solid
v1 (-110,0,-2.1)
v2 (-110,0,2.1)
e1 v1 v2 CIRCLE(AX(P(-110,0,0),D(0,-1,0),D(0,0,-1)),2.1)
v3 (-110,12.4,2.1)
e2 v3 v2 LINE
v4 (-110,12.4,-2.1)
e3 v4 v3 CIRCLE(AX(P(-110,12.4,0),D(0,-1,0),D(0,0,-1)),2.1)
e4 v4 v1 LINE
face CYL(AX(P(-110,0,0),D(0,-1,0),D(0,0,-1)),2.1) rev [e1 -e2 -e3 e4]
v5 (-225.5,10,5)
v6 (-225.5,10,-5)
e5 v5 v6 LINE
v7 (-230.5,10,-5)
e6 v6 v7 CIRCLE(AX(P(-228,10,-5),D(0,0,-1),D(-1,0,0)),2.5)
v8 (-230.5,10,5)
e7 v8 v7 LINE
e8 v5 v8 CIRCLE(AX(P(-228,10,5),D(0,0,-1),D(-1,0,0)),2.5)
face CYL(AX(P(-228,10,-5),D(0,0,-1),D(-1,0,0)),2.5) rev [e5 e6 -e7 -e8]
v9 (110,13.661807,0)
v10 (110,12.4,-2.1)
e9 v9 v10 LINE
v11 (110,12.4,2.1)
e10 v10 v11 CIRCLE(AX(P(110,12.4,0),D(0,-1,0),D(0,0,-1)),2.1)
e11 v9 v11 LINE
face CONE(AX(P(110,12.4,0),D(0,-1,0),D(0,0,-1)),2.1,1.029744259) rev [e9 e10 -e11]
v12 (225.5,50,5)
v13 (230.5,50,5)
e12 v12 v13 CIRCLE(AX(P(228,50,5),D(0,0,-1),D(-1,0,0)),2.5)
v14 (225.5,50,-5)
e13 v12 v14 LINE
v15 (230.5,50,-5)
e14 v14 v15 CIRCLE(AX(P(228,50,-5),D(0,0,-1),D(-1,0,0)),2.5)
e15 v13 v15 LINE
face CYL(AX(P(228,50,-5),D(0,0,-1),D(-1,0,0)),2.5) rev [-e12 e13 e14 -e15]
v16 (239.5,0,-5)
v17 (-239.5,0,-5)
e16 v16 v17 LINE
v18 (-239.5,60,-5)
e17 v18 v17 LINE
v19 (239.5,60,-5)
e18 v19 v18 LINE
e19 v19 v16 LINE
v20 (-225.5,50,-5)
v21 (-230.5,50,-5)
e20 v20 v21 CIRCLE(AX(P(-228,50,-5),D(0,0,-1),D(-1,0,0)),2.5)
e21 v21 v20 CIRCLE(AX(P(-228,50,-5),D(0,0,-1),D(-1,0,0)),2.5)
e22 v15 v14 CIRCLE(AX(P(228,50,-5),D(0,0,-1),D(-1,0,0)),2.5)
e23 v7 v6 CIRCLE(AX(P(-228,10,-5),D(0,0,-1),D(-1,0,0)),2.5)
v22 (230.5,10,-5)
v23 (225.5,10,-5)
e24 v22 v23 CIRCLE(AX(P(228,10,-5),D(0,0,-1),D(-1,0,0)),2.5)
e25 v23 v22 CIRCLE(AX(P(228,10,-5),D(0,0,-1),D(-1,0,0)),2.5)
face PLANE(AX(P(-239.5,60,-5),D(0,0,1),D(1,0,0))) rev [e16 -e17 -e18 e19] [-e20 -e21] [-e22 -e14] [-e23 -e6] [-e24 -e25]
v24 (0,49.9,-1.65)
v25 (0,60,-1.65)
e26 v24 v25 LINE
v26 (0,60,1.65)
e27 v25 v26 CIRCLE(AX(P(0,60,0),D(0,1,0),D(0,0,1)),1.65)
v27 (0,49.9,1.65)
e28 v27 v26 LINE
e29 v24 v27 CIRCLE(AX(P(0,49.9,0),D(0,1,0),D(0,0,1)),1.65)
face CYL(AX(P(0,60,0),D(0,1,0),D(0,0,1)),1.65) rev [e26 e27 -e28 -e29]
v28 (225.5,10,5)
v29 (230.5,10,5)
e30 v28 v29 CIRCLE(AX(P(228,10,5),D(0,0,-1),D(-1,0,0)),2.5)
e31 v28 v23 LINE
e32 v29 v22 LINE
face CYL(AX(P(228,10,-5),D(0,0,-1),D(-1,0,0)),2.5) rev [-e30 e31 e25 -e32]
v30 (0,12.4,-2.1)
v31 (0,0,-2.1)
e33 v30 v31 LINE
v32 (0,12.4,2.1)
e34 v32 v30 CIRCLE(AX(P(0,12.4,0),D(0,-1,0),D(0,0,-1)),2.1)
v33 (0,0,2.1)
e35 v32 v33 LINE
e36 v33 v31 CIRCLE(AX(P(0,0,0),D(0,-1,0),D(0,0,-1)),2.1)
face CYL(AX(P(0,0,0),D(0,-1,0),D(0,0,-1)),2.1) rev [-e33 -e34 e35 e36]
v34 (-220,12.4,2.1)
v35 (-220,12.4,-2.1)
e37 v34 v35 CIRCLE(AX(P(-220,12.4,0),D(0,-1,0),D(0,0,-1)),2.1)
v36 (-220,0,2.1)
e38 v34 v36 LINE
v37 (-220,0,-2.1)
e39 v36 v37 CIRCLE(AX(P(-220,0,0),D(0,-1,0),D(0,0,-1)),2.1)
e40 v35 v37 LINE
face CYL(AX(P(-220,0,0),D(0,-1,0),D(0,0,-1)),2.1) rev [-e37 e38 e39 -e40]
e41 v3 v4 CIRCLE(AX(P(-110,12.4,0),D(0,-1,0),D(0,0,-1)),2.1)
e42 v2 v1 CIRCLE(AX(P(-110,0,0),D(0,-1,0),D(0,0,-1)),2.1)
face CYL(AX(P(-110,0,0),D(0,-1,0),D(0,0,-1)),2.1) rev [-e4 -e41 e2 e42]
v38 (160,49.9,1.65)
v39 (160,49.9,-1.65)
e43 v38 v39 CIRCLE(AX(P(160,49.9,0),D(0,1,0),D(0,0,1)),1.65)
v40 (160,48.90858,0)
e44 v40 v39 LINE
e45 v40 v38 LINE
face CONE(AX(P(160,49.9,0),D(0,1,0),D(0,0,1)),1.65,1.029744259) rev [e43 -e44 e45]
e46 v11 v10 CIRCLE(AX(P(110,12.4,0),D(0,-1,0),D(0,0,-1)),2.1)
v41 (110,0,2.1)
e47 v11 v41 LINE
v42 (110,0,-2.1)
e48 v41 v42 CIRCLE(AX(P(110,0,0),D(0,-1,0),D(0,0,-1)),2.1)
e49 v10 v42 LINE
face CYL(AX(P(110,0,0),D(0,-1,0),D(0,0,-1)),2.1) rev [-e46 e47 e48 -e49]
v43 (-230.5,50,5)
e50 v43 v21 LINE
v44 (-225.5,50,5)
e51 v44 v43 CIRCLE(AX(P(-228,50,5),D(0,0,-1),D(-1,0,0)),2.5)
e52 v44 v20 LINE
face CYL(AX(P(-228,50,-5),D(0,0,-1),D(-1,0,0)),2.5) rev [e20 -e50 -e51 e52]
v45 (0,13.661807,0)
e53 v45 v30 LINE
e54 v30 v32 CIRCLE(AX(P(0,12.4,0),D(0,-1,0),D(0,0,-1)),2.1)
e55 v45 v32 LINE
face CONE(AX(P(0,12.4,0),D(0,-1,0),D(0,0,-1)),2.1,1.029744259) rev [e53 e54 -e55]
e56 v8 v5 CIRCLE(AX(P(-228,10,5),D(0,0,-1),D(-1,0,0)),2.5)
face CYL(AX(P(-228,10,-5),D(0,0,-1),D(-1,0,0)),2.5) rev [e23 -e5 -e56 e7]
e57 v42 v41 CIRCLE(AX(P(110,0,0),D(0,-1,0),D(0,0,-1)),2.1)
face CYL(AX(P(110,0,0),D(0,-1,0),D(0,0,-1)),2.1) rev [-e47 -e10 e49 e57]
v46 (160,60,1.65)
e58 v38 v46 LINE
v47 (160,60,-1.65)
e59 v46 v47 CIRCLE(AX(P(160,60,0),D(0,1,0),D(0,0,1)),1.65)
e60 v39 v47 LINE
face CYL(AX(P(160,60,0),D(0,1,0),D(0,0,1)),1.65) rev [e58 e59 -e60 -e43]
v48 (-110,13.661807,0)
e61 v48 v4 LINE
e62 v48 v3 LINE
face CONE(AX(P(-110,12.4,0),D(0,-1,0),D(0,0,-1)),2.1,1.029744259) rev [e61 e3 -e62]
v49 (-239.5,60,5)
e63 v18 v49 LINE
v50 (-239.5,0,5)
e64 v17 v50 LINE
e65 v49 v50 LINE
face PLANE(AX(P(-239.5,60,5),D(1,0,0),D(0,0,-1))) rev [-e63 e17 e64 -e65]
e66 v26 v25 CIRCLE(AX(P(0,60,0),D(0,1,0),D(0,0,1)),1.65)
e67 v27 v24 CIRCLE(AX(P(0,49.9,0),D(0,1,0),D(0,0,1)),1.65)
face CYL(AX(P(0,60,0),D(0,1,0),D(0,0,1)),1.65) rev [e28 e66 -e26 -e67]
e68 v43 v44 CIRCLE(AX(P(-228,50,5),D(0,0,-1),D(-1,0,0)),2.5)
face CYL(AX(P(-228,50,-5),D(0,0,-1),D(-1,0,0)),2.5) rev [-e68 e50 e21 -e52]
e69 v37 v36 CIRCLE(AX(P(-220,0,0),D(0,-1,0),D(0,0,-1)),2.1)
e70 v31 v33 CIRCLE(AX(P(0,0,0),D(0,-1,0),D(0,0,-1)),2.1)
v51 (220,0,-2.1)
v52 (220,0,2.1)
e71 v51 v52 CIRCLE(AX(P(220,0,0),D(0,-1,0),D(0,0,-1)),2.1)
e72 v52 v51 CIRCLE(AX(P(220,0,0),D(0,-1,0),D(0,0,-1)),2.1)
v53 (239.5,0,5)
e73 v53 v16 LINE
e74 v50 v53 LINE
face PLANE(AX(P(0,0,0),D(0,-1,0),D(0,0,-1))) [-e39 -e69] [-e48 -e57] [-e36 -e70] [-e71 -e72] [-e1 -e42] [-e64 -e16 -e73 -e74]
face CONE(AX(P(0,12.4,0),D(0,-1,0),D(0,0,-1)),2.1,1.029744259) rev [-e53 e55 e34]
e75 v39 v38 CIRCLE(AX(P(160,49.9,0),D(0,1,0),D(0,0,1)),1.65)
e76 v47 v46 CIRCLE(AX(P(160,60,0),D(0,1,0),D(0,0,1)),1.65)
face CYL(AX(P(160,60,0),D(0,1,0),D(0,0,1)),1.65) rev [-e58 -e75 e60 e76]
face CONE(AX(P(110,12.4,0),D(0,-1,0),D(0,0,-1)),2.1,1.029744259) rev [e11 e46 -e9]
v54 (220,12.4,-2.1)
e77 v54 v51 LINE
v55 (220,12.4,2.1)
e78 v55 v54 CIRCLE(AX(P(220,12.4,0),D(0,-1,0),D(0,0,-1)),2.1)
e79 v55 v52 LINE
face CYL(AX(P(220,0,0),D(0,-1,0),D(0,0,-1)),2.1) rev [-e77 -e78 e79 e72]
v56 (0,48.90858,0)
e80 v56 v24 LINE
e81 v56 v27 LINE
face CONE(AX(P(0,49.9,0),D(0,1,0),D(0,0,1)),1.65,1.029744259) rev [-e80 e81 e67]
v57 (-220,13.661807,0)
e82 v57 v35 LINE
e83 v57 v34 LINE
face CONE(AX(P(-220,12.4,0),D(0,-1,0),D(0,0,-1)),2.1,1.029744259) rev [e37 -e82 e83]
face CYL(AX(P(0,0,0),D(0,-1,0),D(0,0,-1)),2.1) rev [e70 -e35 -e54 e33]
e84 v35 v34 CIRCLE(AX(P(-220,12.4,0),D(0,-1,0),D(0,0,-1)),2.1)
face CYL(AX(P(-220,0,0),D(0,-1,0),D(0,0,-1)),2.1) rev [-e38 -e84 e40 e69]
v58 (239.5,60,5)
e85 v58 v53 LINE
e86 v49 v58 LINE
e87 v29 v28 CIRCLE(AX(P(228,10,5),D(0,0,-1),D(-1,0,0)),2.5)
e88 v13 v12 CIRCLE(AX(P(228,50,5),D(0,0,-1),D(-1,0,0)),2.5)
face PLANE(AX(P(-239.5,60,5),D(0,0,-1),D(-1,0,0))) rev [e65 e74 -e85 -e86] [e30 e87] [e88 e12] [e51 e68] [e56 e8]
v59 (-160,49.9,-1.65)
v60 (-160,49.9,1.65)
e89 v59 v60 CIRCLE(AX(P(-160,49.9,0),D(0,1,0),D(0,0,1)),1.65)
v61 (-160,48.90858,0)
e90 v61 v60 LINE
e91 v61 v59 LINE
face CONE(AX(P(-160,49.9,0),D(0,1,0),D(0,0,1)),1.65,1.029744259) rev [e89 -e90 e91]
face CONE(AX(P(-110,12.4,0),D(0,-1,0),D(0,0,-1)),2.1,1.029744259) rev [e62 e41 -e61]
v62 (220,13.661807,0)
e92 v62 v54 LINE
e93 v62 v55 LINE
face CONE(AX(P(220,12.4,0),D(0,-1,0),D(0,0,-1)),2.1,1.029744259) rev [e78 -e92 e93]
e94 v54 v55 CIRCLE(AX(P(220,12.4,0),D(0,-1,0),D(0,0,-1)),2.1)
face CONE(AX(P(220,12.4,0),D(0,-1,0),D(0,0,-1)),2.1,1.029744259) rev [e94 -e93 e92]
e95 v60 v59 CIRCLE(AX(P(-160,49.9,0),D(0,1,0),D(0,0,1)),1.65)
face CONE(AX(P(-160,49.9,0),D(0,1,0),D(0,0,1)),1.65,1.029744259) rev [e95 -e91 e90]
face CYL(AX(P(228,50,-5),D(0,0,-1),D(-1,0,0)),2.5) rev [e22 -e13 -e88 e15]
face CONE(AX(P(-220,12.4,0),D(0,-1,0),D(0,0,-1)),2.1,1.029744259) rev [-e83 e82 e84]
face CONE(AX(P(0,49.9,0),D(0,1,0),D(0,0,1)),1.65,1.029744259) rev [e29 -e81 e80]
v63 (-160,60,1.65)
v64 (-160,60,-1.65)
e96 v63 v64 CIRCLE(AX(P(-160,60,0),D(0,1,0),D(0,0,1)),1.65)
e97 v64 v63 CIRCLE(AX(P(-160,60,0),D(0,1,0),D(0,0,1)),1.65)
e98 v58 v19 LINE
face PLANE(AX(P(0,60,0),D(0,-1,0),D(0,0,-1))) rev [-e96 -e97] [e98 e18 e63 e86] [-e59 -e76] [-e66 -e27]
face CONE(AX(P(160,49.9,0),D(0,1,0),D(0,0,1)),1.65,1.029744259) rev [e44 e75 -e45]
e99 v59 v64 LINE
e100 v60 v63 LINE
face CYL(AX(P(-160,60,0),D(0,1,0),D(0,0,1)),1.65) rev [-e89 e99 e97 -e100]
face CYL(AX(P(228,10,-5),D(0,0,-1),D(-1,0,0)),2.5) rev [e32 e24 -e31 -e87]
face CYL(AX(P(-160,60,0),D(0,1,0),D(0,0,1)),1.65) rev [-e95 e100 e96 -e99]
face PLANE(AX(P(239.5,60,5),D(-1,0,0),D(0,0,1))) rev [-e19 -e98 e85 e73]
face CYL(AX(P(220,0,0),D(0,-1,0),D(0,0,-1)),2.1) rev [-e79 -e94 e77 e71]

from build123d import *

# Parameters (mm, degrees)
SKETCH_1_W             = 479
SKETCH_1_H             = 10
EXTRUDE_1_DEPTH        = 60
HOLE_WIZARD_M5_1_D     = 4.2
HOLE_WIZARD_M5_1_DEPTH = 12.4
HOLE_WIZARD_M5_1_TIP   = 1.2618073
HOLE_WIZARD_M6_1_D     = 5
HOLE_WIZARD_M4_1_D     = 3.3
HOLE_WIZARD_M4_1_DEPTH = 10.1
HOLE_WIZARD_M4_1_TIP   = 0.991420021


with BuildPart() as part:
    # 草图1 → 凸台-拉伸1 (new body)
    with BuildSketch(Plane(origin=(0, 0, 0), x_dir=(1, 0, 0), z_dir=(0, 1, 0))):
        Rectangle(SKETCH_1_W, SKETCH_1_H)
    extrude(amount=EXTRUDE_1_DEPTH)

    # M5 螺纹孔1
    with Locations(Plane(origin=(0, 0, 0), x_dir=(-1, 0, 0), z_dir=(0, -1, 0))):
        with Locations((0, 0), (-110, 0), (-220, 0), (220, 0), (110, 0)):
            Hole(HOLE_WIZARD_M5_1_D / 2, depth=HOLE_WIZARD_M5_1_DEPTH)
            with Locations((0, 0, -(HOLE_WIZARD_M5_1_DEPTH + HOLE_WIZARD_M5_1_TIP / 2))):  # 118° drill point
                Cone(0, HOLE_WIZARD_M5_1_D / 2, HOLE_WIZARD_M5_1_TIP, mode=Mode.SUBTRACT)

    # M6 螺纹孔1 (through all)
    with Locations(Plane(origin=(0, 0, -5), x_dir=(-1, 0, 0), z_dir=(0, 0, -1))):
        with Locations((228, 50), (228, 10), (-228, 10), (-228, 50)):
            Hole(HOLE_WIZARD_M6_1_D / 2)

    # M4 螺纹孔1
    with Locations(Plane(origin=(0, 60, 0), x_dir=(1, 0, 0), z_dir=(0, 1, 0))):
        with Locations((0, 0), (-160, 0), (160, 0)):
            Hole(HOLE_WIZARD_M4_1_D / 2, depth=HOLE_WIZARD_M4_1_DEPTH)
            with Locations((0, 0, -(HOLE_WIZARD_M4_1_DEPTH + HOLE_WIZARD_M4_1_TIP / 2))):  # 118° drill point
                Cone(0, HOLE_WIZARD_M4_1_D / 2, HOLE_WIZARD_M4_1_TIP, mode=Mode.SUBTRACT)


solid = part.part
